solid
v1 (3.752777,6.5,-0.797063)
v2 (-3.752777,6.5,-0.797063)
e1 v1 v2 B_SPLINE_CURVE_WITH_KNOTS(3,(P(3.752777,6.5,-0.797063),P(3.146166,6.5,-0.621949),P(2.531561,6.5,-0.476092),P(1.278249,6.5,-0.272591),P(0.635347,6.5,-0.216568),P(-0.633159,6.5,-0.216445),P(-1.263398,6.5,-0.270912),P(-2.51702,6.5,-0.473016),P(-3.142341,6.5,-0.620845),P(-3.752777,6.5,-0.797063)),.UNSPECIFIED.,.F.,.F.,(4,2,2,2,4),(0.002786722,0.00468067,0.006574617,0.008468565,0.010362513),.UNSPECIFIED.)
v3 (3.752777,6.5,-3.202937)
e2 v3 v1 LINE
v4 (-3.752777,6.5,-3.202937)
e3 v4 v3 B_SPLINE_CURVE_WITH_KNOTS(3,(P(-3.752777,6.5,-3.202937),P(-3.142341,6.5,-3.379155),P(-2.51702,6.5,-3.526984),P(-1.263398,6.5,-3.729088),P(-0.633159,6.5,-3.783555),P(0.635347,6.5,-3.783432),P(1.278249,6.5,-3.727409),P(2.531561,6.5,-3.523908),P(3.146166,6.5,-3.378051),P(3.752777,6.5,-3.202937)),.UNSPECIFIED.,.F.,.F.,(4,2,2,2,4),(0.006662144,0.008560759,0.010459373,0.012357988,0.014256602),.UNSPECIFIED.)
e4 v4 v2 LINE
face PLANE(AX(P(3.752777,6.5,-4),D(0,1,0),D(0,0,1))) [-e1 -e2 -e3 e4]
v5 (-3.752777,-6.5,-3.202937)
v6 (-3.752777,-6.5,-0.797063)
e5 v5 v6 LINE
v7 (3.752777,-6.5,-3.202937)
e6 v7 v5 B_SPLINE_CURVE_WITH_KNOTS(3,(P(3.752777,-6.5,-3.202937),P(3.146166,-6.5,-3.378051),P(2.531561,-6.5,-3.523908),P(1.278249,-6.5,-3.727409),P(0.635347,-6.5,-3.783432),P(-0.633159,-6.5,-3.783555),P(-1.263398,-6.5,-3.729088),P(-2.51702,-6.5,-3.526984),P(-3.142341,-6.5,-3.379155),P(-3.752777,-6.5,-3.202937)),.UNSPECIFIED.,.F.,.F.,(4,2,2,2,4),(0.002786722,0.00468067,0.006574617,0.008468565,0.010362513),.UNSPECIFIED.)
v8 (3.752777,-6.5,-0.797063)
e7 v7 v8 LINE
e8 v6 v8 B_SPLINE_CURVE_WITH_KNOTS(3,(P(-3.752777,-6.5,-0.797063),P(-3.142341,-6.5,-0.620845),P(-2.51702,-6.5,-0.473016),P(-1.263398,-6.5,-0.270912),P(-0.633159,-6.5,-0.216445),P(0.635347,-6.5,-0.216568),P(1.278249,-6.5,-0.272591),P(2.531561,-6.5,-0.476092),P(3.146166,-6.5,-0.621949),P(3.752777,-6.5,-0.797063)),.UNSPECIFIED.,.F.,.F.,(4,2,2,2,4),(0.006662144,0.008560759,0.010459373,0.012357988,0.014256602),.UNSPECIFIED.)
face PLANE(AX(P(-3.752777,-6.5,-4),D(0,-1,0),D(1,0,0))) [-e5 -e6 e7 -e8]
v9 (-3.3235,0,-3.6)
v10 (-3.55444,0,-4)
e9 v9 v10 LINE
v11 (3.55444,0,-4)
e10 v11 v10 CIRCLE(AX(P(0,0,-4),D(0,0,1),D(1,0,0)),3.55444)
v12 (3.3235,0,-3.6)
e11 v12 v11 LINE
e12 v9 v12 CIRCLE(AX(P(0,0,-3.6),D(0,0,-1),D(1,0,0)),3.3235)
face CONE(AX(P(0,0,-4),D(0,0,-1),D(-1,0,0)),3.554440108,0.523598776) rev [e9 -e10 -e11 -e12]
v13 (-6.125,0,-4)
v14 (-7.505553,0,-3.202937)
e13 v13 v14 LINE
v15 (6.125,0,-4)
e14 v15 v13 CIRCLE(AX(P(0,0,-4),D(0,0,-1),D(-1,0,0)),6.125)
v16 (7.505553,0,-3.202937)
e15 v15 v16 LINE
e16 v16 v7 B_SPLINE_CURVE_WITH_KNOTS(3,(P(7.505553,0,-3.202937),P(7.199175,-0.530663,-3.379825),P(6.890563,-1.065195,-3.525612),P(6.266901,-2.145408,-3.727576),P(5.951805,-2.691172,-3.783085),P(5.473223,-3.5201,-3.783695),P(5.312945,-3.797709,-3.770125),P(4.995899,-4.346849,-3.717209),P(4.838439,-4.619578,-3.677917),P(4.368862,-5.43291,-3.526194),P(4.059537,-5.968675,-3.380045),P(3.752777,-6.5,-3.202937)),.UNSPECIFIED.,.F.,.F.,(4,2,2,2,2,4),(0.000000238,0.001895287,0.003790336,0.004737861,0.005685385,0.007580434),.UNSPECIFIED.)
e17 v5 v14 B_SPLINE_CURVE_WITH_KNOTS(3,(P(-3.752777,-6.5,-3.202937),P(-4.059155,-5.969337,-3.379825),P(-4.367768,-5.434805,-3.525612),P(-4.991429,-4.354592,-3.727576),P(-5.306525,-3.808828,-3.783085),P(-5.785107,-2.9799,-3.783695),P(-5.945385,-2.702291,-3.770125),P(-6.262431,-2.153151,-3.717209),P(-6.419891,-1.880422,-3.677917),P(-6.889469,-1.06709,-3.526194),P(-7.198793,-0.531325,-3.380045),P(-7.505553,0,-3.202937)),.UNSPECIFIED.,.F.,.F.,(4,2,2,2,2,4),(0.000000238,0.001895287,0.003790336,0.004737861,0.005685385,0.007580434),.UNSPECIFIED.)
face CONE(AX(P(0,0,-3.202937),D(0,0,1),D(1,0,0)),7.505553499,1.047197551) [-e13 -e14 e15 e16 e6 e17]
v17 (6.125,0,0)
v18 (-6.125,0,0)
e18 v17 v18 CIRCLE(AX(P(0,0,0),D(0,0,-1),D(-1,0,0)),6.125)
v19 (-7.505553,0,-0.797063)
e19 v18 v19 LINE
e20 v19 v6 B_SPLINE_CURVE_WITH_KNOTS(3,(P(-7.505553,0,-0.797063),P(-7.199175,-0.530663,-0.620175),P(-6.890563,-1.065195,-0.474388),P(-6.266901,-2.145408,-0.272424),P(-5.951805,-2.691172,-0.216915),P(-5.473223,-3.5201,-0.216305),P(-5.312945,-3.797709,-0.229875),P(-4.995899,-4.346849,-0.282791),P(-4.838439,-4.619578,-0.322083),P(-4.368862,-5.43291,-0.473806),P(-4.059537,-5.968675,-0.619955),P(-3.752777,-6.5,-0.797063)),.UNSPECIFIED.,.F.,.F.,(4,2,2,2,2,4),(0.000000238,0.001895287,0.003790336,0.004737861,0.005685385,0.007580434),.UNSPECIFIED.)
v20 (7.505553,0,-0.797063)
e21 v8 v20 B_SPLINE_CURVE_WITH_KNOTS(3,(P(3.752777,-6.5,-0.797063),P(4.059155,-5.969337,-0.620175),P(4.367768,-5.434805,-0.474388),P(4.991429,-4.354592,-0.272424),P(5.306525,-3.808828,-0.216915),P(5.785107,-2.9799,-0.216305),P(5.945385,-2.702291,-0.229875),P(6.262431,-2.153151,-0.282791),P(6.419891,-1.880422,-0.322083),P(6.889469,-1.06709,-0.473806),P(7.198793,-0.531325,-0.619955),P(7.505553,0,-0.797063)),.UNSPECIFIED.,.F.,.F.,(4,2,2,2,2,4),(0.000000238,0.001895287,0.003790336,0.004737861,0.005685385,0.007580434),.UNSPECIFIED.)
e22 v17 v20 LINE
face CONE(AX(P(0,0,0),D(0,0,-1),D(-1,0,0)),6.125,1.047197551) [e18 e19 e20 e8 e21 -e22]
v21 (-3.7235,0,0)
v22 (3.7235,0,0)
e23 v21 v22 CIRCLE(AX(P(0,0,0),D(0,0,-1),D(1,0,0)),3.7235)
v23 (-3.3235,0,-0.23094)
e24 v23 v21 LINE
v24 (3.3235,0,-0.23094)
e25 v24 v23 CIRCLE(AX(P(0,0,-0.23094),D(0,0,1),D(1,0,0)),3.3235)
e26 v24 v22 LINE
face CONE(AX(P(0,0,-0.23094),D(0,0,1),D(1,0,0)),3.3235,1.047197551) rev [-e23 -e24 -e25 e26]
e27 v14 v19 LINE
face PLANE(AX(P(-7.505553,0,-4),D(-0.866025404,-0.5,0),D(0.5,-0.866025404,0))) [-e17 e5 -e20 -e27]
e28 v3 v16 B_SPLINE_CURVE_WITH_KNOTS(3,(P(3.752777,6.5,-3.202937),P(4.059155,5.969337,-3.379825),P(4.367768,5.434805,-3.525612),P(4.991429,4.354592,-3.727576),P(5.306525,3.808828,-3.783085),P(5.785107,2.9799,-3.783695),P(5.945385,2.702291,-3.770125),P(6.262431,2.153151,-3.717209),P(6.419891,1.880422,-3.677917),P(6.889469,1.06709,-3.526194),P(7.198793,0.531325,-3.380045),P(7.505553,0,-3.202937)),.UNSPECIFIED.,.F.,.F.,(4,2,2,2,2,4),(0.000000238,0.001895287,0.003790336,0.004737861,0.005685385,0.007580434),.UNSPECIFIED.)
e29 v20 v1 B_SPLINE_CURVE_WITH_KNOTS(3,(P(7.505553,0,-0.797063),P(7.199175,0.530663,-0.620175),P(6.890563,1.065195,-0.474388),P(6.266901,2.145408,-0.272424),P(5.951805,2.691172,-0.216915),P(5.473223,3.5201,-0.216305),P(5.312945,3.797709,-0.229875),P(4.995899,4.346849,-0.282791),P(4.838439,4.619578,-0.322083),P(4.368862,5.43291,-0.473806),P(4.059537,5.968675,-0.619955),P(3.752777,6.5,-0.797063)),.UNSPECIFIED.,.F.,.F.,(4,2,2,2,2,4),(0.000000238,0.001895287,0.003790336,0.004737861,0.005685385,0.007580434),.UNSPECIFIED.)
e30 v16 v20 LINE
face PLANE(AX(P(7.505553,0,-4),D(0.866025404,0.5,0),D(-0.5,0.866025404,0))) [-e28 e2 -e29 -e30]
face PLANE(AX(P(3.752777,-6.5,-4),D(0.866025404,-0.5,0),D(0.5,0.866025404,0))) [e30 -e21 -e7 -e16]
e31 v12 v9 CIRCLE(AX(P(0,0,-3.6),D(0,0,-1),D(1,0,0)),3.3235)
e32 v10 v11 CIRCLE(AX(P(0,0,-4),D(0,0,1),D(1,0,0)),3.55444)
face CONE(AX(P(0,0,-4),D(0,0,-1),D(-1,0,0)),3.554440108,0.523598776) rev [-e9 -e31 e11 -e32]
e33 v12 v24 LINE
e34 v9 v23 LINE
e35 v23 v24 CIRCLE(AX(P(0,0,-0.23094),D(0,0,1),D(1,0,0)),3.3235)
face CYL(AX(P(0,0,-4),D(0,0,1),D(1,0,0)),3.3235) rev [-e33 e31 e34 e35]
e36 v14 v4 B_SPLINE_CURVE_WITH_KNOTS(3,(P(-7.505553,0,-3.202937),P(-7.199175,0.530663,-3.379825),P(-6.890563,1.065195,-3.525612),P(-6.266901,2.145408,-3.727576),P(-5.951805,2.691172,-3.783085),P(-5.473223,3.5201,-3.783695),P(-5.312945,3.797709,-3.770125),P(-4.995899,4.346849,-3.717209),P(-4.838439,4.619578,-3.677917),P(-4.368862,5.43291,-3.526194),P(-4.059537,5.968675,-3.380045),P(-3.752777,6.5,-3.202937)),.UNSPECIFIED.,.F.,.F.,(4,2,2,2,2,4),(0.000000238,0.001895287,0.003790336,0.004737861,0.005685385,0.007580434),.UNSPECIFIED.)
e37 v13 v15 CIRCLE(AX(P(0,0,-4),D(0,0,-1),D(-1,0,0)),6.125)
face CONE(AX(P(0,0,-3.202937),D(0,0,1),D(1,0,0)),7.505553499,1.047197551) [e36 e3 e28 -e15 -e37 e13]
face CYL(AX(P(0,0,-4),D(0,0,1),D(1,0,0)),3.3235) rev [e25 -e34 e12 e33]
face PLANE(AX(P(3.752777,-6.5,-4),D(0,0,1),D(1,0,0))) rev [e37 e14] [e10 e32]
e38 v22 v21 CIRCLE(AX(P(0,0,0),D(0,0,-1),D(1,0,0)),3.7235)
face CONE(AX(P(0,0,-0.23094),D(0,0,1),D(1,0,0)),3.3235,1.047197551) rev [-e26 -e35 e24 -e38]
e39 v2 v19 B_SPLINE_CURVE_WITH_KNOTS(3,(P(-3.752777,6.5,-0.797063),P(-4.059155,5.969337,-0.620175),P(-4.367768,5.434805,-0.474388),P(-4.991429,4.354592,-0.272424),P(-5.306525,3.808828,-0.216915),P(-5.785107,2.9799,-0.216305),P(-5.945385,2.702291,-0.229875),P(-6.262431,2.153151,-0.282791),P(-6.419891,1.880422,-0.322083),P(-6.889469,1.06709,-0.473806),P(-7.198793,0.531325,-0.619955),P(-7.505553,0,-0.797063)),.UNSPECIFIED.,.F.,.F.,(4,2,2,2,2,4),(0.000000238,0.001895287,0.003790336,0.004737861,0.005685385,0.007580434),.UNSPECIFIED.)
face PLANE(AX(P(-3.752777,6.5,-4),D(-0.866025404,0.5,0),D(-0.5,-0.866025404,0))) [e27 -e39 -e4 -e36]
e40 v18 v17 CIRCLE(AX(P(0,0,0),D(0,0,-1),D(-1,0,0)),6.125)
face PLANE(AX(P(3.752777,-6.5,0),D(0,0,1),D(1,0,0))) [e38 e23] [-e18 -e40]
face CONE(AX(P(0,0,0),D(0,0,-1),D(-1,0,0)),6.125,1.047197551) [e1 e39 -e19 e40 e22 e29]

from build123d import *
from OCP.BRepFilletAPI import BRepFilletAPI_MakeChamfer

# Parameters (mm, degrees)
SKETCH1_R        = 3.3235
BASENUT_DEPTH    = 4
ENDCHAMFER_SIZE  = 0.4
ENDCHAMFER_SIZE2 = 0.230940108


with BuildPart() as part:
    # Sketch1 → BaseNut (new body)
    with BuildSketch(Plane.XY):
        Polygon((3.75277675, -6.5), (7.505553499, 0), (3.75277675, 6.5), (-3.75277675, 6.5), (-7.505553499, 0), (-3.75277675, -6.5), align=None)
        Circle(SKETCH1_R, mode=Mode.SUBTRACT)
    extrude(amount=-BASENUT_DEPTH)

    # Sketch2 → Double-Chamfer (revolve, cut)
    with BuildSketch(Plane(origin=(0, 0, 0), x_dir=(1, 0, 0), z_dir=(0, 1, 0))):
        Polygon((-7.505553499, 4), (-6.125, 4), (-7.505553499, 3.202937065), align=None)
        Polygon((-7.505553499, 0.797062935), (-7.505553499, 0), (-6.125, 0), align=None)
    revolve(axis=Axis((0, 0, -3.375940562), (0, 0, 1)), mode=Mode.SUBTRACT)

    # EndChamfer: one chamfer whose edges measure the first distance from different faces: ONE call of the kernel's chamfer builder (chamfer() names one face for all edges)
    endchamfer_edges_1 = [part.edges().sort_by_distance(p)[0] for p in [
        (-3.3235, 0, -4),
    ]]
    endchamfer_side_1 = [part.faces().sort_by_distance(p)[0] for p in [
        (-3.3235, 0, -2),
    ]]
    endchamfer_edges_2 = [part.edges().sort_by_distance(p)[0] for p in [
        (-3.3235, 0, 0),
    ]]
    endchamfer_side_2 = [part.faces().sort_by_distance(p)[0] for p in [
        (5.951758839, 0, 0),
    ]]
    endchamfer = BRepFilletAPI_MakeChamfer(part.part.solid().wrapped)
    for e in endchamfer_edges_1:
        endchamfer.Add(ENDCHAMFER_SIZE, ENDCHAMFER_SIZE2, e.wrapped, endchamfer_side_1[0].wrapped)  # the first distance lies on this face
    for e in endchamfer_edges_2:
        endchamfer.Add(ENDCHAMFER_SIZE, ENDCHAMFER_SIZE2, e.wrapped, endchamfer_side_2[0].wrapped)  # the first distance lies on this face
    add(Compound.cast(endchamfer.Shape()), mode=Mode.REPLACE)


solid = part.part
